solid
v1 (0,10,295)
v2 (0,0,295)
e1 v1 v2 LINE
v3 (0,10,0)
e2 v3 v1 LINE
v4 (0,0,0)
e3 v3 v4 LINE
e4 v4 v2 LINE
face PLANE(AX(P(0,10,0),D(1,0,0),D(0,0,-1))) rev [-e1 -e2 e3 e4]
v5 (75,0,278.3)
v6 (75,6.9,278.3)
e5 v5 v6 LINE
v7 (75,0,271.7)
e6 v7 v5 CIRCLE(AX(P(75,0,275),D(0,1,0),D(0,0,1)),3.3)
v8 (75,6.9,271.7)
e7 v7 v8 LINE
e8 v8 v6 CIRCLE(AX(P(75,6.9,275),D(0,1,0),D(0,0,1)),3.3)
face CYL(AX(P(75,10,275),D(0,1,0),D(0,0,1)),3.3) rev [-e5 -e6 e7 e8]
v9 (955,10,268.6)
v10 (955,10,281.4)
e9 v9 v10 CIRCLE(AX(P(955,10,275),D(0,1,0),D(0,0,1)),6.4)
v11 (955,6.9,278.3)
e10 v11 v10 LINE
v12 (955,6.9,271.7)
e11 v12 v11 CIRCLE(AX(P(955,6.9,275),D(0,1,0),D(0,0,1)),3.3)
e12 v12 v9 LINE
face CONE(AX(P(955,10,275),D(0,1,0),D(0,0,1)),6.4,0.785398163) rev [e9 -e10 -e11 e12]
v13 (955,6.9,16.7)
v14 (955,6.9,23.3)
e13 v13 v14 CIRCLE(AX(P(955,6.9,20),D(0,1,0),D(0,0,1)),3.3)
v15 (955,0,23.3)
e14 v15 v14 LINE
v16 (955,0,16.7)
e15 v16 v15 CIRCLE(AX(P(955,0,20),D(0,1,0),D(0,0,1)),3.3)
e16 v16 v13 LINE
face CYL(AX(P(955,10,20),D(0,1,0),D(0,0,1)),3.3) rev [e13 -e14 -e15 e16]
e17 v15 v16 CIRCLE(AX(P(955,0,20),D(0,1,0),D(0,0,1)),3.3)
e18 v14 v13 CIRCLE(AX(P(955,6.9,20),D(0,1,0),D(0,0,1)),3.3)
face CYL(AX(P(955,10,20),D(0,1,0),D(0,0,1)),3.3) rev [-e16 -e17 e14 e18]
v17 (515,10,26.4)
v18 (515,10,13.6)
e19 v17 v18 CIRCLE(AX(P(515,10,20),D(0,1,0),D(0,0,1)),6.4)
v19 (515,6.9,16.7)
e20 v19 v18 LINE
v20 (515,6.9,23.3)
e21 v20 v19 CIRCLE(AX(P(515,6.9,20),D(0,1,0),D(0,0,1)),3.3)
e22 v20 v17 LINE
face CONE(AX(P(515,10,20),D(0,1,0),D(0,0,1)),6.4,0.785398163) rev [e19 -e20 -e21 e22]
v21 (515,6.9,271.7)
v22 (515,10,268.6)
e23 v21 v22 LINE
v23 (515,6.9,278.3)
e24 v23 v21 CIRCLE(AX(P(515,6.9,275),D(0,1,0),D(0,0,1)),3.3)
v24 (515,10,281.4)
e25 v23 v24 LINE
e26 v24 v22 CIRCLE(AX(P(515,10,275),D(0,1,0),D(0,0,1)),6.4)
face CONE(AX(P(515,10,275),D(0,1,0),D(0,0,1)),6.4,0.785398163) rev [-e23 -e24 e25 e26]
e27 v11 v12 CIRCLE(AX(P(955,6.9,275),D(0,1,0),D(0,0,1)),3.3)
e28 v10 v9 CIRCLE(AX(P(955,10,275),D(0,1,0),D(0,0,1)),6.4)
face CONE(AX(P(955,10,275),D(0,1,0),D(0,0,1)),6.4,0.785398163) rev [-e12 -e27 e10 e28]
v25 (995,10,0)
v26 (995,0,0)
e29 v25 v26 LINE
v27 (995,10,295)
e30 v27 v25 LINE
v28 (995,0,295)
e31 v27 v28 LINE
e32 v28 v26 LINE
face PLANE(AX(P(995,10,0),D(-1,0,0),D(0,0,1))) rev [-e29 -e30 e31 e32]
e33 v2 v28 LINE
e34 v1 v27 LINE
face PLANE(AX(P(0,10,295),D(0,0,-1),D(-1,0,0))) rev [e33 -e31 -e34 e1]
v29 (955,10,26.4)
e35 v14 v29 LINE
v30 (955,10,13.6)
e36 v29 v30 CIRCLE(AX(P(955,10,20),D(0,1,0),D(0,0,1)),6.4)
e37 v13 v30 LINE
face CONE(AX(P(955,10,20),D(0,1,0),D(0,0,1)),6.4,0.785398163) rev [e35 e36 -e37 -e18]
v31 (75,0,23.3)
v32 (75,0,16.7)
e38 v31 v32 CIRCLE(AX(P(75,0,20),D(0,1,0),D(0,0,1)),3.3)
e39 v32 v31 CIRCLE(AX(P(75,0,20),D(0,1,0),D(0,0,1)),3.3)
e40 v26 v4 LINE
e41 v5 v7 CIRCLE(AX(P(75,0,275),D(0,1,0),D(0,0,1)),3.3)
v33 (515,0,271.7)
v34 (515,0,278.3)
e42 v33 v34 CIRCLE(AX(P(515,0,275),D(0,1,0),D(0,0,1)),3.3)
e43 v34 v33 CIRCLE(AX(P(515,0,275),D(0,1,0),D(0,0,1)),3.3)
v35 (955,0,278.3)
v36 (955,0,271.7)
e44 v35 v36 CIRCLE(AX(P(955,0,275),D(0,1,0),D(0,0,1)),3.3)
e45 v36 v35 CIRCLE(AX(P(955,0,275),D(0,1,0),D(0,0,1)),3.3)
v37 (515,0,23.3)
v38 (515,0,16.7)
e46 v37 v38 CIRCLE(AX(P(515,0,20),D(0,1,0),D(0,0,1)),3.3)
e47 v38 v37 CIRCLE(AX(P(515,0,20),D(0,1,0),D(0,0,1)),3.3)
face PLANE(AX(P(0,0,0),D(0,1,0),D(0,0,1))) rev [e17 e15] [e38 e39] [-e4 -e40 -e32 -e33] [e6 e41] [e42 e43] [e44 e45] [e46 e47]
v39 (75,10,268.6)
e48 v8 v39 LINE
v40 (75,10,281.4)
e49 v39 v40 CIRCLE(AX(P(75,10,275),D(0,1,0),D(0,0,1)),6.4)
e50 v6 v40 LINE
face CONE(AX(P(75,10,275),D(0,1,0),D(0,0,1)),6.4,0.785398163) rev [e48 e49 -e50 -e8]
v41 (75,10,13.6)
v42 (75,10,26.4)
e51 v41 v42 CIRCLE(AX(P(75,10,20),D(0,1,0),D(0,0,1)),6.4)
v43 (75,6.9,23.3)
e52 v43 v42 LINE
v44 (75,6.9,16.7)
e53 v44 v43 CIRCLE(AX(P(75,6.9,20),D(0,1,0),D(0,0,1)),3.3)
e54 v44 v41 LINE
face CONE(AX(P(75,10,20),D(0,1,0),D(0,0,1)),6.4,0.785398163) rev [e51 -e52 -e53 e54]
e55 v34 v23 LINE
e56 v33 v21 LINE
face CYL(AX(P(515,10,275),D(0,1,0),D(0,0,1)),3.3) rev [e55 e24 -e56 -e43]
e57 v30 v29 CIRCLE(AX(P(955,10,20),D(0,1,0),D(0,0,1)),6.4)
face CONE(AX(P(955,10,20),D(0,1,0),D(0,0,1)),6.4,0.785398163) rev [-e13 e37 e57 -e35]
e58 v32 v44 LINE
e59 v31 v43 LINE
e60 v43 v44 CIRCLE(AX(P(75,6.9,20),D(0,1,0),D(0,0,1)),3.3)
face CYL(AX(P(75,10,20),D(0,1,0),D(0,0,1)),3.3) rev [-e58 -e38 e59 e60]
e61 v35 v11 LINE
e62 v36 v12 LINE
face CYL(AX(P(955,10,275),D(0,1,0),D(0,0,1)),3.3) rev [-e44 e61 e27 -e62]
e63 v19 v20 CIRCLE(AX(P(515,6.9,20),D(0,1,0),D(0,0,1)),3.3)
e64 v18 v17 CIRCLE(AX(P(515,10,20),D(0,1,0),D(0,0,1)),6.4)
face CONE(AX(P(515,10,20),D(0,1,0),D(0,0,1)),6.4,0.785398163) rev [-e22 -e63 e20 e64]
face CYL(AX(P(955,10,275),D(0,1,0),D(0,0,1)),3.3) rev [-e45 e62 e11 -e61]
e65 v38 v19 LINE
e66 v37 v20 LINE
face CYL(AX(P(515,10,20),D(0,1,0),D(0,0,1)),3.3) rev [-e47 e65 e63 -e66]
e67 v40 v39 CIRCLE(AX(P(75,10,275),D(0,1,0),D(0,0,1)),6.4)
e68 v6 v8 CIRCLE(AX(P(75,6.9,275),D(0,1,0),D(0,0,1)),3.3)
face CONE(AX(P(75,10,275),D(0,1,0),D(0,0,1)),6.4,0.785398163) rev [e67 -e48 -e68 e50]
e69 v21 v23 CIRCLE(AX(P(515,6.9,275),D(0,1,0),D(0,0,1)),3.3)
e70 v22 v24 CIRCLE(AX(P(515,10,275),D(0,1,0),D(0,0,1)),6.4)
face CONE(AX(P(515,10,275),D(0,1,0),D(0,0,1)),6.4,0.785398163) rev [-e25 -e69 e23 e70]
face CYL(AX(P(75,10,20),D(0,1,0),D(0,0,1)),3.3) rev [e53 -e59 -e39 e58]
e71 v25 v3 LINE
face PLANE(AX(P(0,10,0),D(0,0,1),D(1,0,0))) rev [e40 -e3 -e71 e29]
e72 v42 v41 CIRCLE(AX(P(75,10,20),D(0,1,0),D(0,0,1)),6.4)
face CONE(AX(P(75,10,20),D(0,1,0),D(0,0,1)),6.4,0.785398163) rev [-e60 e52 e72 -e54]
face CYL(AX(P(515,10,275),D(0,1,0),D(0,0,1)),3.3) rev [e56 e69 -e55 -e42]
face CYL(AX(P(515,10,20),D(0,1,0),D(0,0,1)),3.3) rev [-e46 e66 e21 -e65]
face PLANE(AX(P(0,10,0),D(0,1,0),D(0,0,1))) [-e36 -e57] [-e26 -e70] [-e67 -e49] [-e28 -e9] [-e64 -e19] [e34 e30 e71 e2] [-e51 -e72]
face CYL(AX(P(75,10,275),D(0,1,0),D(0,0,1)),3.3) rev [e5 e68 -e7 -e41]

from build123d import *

# Parameters (mm, degrees)
SKETCH1_W                                         = 995
SKETCH1_H                                         = 295
BOSS_EXTRUDE1_DEPTH                               = 10
HOLE_SIZE_BASED_HEXALOBULAR_SOCKET_SE_D           = 6.6
HOLE_SIZE_BASED_HEXALOBULAR_SOCKET_SE_DEPTH       = 19.75
HOLE_SIZE_BASED_HEXALOBULAR_SOCKET_SE_CSINK_D     = 12.8
HOLE_SIZE_BASED_HEXALOBULAR_SOCKET_SE_CSINK_ANGLE = 90
HOLE_SIZE_BASED_HEXALOBULAR_SOCKET_SE_TIP         = 1.982840043


with BuildPart() as part:
    # Sketch1 → Boss-Extrude1 (new body)
    with BuildSketch(Plane(origin=(0, 0, 0), x_dir=(1, 0, 0), z_dir=(0, 1, 0))):
        with Locations((497.5, -147.5)):
            Rectangle(SKETCH1_W, SKETCH1_H)
    extrude(amount=BOSS_EXTRUDE1_DEPTH)

    # Hole Size (% based) Hexalobular Socket Semi-Countersunk Screw Type1
    with Locations(Plane(origin=(0, 10, 0), x_dir=(1, 0, 0), z_dir=(0, 1, 0))):
        with Locations((75, -20), (75, -275), (515, -20), (515, -275), (955, -275), (955, -20)):
            CounterSinkHole(HOLE_SIZE_BASED_HEXALOBULAR_SOCKET_SE_D / 2, HOLE_SIZE_BASED_HEXALOBULAR_SOCKET_SE_CSINK_D / 2, depth=HOLE_SIZE_BASED_HEXALOBULAR_SOCKET_SE_DEPTH, counter_sink_angle=HOLE_SIZE_BASED_HEXALOBULAR_SOCKET_SE_CSINK_ANGLE)
            with Locations((0, 0, -(HOLE_SIZE_BASED_HEXALOBULAR_SOCKET_SE_DEPTH + HOLE_SIZE_BASED_HEXALOBULAR_SOCKET_SE_TIP / 2))):  # 118° drill point
                Cone(0, HOLE_SIZE_BASED_HEXALOBULAR_SOCKET_SE_D / 2, HOLE_SIZE_BASED_HEXALOBULAR_SOCKET_SE_TIP, mode=Mode.SUBTRACT)


solid = part.part
